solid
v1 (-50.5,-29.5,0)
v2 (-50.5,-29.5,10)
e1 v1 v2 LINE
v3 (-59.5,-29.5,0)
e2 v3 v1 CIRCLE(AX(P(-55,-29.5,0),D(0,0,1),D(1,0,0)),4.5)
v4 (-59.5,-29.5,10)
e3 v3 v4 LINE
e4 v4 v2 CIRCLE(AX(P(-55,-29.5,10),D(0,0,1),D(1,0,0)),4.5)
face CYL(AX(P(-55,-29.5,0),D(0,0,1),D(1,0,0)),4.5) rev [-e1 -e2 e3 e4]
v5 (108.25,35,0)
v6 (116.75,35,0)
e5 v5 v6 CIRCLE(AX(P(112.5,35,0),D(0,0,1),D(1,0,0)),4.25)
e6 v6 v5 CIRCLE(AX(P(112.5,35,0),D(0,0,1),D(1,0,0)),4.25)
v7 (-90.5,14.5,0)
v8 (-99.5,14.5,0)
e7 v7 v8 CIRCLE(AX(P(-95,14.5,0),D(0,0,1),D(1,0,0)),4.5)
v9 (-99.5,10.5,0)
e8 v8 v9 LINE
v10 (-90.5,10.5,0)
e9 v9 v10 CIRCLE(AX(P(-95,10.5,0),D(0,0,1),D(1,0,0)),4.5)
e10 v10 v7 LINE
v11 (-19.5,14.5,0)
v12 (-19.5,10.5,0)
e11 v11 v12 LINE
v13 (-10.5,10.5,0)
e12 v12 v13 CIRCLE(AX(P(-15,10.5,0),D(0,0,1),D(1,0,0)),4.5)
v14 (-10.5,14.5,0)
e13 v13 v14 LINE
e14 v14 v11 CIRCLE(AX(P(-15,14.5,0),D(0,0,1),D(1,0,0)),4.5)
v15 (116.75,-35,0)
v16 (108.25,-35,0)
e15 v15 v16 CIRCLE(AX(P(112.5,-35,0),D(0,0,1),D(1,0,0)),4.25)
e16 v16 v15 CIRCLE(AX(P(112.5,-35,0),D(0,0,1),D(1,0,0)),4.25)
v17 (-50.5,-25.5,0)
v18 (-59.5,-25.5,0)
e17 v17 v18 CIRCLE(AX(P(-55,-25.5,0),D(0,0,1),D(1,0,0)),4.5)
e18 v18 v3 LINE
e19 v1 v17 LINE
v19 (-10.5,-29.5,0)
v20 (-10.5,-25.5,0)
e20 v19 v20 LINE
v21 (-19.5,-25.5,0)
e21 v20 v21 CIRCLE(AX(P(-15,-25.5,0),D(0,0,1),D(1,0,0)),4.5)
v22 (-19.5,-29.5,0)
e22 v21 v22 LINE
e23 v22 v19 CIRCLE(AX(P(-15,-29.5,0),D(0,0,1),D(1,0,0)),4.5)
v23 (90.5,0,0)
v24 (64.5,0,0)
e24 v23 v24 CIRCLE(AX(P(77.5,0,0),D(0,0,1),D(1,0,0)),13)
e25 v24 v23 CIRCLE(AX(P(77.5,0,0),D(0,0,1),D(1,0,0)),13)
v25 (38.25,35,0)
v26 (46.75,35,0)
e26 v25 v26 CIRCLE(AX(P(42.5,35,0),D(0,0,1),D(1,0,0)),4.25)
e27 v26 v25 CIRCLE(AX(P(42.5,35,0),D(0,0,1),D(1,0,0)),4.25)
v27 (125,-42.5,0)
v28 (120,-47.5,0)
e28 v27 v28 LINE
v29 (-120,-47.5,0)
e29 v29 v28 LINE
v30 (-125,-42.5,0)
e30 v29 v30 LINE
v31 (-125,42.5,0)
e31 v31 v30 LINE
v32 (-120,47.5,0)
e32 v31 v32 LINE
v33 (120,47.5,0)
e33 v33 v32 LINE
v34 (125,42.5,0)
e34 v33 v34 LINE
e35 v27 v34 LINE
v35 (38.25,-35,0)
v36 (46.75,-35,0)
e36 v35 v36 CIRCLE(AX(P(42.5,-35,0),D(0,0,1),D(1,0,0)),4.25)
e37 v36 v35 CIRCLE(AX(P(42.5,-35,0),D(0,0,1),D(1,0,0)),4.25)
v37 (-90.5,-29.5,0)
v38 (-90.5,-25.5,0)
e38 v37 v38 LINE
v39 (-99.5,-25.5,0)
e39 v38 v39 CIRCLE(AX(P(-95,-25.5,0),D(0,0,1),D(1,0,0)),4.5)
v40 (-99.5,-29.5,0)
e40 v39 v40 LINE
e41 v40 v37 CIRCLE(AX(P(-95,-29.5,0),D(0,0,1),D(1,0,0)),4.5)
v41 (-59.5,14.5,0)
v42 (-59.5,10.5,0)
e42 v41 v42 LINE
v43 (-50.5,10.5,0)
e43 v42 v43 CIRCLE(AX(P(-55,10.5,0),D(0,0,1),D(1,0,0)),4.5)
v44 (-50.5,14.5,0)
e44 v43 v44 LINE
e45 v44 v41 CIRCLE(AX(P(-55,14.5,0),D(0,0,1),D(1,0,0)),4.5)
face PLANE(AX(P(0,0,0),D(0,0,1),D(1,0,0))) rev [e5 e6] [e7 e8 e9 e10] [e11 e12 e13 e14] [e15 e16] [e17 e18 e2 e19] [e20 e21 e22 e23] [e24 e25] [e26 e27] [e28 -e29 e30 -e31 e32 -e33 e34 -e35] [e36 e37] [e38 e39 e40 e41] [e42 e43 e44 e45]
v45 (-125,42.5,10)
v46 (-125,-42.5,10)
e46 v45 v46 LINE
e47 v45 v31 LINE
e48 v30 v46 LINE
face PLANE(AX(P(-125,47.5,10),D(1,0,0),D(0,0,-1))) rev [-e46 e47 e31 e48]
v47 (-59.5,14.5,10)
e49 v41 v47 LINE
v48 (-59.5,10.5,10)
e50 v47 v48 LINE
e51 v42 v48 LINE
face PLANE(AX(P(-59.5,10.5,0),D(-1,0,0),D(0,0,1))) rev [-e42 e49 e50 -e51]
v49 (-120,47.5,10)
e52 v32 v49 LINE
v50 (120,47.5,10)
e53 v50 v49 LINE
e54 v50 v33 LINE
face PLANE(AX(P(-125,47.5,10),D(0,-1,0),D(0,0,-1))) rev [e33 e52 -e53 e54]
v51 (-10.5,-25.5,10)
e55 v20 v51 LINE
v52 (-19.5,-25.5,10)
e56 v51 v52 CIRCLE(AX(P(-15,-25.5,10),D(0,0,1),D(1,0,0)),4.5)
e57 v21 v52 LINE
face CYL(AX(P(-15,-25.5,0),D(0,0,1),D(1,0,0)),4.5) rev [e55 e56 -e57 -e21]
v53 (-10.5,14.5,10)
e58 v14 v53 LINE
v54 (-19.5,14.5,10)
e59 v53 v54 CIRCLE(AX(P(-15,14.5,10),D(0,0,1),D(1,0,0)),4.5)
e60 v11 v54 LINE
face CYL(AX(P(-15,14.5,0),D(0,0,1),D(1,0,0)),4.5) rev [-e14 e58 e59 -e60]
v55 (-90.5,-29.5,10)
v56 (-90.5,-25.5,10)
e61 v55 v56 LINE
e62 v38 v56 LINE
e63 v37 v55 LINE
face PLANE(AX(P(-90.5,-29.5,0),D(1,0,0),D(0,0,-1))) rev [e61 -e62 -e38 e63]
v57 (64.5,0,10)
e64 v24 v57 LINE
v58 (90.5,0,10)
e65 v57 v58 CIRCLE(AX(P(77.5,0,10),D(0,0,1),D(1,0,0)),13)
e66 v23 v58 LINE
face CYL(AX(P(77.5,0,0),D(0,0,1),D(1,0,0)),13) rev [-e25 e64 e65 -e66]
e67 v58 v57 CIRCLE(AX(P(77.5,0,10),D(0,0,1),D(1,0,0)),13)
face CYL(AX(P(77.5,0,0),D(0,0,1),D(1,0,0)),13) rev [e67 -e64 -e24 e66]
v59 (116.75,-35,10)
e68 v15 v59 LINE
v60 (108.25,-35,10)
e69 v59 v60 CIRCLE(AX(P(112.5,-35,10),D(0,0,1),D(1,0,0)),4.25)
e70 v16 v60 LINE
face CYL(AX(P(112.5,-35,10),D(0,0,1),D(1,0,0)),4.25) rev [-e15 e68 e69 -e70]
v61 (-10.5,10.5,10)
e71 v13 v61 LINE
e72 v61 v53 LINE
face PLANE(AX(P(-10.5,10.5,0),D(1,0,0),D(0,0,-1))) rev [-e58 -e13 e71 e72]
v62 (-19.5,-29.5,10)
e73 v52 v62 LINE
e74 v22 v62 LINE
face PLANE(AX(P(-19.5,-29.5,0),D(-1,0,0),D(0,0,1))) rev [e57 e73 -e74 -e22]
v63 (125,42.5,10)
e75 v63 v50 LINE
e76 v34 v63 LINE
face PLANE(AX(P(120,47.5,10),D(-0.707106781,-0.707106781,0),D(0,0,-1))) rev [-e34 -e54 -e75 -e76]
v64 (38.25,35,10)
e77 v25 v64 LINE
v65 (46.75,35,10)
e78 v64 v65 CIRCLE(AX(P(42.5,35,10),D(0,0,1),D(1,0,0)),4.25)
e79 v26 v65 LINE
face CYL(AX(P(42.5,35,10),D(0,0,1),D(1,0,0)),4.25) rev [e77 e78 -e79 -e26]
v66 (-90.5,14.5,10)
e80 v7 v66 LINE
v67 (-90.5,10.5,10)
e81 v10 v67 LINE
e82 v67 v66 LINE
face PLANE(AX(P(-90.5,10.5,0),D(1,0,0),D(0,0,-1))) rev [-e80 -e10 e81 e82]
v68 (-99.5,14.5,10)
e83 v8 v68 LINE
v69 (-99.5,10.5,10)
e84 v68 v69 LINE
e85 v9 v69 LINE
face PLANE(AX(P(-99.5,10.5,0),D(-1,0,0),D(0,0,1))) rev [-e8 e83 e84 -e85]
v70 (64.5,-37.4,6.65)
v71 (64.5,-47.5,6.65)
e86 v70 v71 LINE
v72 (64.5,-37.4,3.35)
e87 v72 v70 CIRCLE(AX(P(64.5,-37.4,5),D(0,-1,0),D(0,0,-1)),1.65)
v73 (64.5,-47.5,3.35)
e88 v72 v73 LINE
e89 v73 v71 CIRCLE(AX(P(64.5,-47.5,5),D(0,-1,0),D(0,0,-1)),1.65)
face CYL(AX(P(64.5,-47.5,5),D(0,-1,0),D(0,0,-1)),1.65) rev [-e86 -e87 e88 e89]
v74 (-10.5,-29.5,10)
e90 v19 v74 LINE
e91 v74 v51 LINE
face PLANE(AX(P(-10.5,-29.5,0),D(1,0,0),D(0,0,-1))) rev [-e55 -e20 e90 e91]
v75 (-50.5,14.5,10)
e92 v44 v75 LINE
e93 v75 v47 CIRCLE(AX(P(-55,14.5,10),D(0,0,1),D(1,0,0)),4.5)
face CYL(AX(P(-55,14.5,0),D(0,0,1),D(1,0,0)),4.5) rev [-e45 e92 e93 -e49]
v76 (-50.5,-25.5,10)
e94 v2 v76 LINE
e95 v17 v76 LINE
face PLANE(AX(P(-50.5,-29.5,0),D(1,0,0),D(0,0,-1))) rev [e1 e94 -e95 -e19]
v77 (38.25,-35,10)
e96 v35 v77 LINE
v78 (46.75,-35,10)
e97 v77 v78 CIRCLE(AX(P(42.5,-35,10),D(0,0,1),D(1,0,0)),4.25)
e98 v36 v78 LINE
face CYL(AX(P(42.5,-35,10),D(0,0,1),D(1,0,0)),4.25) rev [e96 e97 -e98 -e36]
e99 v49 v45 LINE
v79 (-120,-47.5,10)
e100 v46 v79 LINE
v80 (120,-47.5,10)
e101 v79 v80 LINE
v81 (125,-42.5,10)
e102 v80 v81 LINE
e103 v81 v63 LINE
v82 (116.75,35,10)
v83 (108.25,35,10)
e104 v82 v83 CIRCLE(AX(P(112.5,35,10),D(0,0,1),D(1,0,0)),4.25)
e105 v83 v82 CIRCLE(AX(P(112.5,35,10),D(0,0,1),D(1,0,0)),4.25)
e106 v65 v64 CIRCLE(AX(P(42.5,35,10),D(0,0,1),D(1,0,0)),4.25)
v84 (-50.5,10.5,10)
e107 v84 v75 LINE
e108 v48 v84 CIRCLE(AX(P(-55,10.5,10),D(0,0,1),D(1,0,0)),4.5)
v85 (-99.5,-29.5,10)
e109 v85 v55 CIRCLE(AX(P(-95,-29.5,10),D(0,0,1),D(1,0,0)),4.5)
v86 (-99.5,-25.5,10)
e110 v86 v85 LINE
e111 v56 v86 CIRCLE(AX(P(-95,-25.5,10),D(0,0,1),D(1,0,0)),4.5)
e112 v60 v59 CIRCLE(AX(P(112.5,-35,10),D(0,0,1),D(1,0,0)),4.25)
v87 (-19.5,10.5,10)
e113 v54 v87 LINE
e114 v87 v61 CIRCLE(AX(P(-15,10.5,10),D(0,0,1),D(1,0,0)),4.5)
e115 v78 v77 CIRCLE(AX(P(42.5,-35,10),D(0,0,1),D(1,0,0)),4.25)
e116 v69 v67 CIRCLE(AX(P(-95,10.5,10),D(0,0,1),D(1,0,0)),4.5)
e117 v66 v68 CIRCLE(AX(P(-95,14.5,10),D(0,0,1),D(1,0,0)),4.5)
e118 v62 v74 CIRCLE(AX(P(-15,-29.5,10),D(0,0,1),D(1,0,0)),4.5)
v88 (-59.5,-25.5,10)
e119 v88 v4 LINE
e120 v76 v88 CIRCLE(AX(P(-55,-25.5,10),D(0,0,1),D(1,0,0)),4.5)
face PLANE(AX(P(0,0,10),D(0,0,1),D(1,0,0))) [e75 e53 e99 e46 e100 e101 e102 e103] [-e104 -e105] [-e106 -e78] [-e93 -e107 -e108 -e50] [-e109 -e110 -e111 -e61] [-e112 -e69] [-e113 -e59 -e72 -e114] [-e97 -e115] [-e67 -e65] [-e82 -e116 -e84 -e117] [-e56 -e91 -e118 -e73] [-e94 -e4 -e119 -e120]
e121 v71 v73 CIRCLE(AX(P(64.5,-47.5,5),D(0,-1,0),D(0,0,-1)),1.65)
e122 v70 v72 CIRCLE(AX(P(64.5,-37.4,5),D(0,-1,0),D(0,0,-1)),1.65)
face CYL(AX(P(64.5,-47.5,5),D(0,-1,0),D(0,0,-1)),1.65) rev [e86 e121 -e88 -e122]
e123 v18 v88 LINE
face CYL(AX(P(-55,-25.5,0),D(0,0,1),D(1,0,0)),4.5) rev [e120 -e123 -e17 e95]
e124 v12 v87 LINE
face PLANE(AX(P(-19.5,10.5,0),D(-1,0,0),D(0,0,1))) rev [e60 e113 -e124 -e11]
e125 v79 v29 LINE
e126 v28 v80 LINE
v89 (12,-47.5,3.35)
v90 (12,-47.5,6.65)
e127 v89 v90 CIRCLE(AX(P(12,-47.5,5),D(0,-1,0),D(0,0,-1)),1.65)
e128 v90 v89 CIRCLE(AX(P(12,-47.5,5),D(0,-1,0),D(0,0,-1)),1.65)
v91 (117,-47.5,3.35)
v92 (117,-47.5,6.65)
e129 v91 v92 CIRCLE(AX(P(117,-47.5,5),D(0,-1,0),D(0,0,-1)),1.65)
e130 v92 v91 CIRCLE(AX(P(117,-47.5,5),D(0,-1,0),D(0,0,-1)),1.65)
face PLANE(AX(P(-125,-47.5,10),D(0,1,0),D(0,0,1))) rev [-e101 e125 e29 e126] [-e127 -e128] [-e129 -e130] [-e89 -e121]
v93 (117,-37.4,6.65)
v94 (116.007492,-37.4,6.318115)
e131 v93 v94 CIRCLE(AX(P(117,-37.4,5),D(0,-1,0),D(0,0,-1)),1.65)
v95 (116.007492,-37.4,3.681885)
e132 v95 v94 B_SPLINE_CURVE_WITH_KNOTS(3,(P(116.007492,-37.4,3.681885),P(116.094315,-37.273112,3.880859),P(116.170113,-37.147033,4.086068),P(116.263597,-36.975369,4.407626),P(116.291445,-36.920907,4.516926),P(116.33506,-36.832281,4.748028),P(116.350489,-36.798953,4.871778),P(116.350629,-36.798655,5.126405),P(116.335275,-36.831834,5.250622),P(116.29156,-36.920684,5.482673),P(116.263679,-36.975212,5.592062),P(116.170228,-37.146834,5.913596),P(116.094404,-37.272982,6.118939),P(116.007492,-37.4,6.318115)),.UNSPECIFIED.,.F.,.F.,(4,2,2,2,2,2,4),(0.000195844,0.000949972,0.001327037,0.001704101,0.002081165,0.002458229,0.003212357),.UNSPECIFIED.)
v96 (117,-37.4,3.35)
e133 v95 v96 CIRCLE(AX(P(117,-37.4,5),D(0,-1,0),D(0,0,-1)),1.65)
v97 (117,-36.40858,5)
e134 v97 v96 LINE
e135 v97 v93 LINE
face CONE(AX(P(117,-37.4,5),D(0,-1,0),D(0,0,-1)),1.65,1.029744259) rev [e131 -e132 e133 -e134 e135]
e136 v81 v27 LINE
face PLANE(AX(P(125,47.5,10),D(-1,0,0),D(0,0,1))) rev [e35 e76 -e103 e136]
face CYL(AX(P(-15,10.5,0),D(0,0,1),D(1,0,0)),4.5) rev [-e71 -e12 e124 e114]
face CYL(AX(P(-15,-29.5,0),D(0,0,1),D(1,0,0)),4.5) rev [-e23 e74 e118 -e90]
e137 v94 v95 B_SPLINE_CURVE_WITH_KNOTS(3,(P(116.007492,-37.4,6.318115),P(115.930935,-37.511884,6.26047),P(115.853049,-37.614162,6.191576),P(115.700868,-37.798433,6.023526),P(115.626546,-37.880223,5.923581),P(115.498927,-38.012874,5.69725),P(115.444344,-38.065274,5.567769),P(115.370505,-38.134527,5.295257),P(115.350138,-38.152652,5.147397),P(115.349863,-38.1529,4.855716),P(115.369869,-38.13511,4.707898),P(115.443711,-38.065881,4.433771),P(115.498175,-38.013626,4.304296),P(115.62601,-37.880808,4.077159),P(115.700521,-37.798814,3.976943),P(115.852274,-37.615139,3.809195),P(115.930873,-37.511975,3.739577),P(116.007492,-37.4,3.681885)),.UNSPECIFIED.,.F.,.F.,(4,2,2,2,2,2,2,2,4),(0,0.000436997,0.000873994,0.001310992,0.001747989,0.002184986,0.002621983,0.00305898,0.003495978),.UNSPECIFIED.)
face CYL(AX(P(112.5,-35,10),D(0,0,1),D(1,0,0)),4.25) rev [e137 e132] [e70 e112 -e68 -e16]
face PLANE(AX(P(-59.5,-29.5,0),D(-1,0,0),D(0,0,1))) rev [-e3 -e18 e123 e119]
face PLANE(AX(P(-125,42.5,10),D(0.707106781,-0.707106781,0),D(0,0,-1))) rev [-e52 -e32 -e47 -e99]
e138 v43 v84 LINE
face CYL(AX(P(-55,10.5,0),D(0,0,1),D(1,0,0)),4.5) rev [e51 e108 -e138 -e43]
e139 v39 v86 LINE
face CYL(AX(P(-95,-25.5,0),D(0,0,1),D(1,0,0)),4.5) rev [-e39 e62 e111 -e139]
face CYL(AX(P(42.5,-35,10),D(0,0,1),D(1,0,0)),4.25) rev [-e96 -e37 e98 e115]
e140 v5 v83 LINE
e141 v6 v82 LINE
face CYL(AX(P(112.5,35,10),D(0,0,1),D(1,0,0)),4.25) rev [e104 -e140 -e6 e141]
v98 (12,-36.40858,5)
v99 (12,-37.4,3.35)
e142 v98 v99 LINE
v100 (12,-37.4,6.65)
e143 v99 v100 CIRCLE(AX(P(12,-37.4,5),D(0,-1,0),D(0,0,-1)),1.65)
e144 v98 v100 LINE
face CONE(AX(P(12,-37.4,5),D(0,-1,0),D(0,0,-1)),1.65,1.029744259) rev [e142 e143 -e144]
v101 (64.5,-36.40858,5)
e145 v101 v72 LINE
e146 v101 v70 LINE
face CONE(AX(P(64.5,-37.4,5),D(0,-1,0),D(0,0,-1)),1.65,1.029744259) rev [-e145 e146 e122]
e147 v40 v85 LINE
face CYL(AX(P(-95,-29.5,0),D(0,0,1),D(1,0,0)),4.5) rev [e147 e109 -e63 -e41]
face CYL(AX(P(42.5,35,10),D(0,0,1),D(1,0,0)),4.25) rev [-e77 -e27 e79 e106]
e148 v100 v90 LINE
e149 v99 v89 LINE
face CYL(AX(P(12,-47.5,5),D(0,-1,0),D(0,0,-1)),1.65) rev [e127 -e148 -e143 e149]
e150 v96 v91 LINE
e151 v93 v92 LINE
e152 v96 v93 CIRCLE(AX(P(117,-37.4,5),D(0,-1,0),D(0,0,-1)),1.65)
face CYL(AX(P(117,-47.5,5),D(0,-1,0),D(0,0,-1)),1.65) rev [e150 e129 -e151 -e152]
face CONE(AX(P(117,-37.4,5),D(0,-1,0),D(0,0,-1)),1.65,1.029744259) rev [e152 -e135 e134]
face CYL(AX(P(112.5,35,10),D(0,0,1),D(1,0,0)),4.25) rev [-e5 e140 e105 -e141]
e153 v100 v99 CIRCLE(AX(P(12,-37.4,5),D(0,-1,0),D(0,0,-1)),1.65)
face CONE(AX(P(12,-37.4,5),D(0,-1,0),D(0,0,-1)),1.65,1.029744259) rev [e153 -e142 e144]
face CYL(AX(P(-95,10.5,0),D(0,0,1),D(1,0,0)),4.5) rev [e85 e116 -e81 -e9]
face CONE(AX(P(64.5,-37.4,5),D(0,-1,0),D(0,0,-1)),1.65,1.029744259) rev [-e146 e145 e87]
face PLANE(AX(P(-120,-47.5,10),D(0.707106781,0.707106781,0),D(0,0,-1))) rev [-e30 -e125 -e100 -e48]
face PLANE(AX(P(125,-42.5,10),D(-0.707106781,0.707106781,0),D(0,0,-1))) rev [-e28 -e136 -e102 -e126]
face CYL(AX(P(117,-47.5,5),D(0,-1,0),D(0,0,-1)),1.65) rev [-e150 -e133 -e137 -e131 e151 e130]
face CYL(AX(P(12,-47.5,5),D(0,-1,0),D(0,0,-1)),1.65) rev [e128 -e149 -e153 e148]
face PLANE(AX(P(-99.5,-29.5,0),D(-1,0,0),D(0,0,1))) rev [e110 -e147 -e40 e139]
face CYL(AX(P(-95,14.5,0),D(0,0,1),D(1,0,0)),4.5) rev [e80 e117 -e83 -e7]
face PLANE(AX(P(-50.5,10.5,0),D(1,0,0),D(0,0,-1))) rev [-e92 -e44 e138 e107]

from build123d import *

# Parameters (mm, degrees)
SKETCH_1_W                  = 250
SKETCH_1_H                  = 95
EXTRUDE_1_DEPTH             = 10
CUT_EXTRUDE_2_DEPTH         = 135.094183319
PATTERN_LINEAR_1_COUNT      = 2
PATTERN_LINEAR_1_PITCH      = 40
PATTERN_LINEAR_1_COUNT_DIR2 = 2
PATTERN_LINEAR_1_PITCH_DIR2 = 40
PATTERN_LINEAR_2_COUNT      = 2
PATTERN_LINEAR_2_PITCH      = 40
PATTERN_LINEAR_2_COUNT_DIR2 = 2
PATTERN_LINEAR_2_PITCH_DIR2 = 40
CHAMFER_1_SIZE              = 5
HOLE_WIZARD_M10_3_D         = 8.5
HOLE_WIZARD_M10_3_DEPTH     = 24.5
HOLE_WIZARD_M10_3_TIP       = 2.553657631
SKETCH_12_R                 = 13
CUT_EXTRUDE_5_DEPTH         = 135.094183319
HOLE_WIZARD_M4_1_D          = 3.3
HOLE_WIZARD_M4_1_DEPTH      = 10.1
HOLE_WIZARD_M4_1_TIP        = 0.991420021


with BuildPart() as part:
    # 草图1 → 凸台-拉伸1 (new body)
    with BuildSketch(Plane.XY):
        Rectangle(SKETCH_1_W, SKETCH_1_H)
    extrude(amount=EXTRUDE_1_DEPTH)

    # 草图3 → 切除-拉伸2 (cut, through all)
    with BuildSketch(Plane.XY.offset(10)):
        with BuildLine():
            Line((-59.5, -29.5), (-59.5, -25.5))
            ThreePointArc((-59.5, -25.5), (-55, -21), (-50.5, -25.5))
            Line((-50.5, -25.5), (-50.5, -29.5))
            ThreePointArc((-50.5, -29.5), (-55, -34), (-59.5, -29.5))
        make_face()
    cut_extrude_2 = extrude(amount=-CUT_EXTRUDE_2_DEPTH, mode=Mode.SUBTRACT)

    # 阵列(线性)1: Cut-Extrude 2 2 × 2
    with Locations(*[(i * PATTERN_LINEAR_1_PITCH, j * PATTERN_LINEAR_1_PITCH_DIR2, 0) for i in range(PATTERN_LINEAR_1_COUNT) for j in range(PATTERN_LINEAR_1_COUNT_DIR2) if (i, j) != (0, 0)]):
        add(cut_extrude_2, mode=Mode.SUBTRACT)

    # 阵列(线性)2: Cut-Extrude 2 2 × 2
    with Locations(*[(-i * PATTERN_LINEAR_2_PITCH, j * PATTERN_LINEAR_2_PITCH_DIR2, 0) for i in range(PATTERN_LINEAR_2_COUNT) for j in range(PATTERN_LINEAR_2_COUNT_DIR2) if (i, j) != (0, 0)]):
        add(cut_extrude_2, mode=Mode.SUBTRACT)

    # 倒角1
    chamfer_1_edges = [part.edges().sort_by_distance(p)[0] for p in [
        (125, -47.5, 5),
        (-125, -47.5, 5),
        (-125, 47.5, 5),
        (125, 47.5, 5),
    ]]
    chamfer(chamfer_1_edges, length=CHAMFER_1_SIZE)

    # M10 螺纹孔3
    with Locations(Plane(origin=(42.5, 35, 10), x_dir=(1, 0, 0), z_dir=(0, 0, 1))):
        with Locations((0, 0), (70, 0), (70, -70), (0, -70)):
            Hole(HOLE_WIZARD_M10_3_D / 2, depth=HOLE_WIZARD_M10_3_DEPTH)
            with Locations((0, 0, -(HOLE_WIZARD_M10_3_DEPTH + HOLE_WIZARD_M10_3_TIP / 2))):  # 118° drill point
                Cone(0, HOLE_WIZARD_M10_3_D / 2, HOLE_WIZARD_M10_3_TIP, mode=Mode.SUBTRACT)

    # 草图12 → 切除-拉伸5 (cut, through all)
    with BuildSketch(Plane.XY.offset(10)):
        with Locations((77.5, 0)):
            Circle(SKETCH_12_R)
    extrude(amount=-CUT_EXTRUDE_5_DEPTH, mode=Mode.SUBTRACT)

    # M4 螺纹孔1
    with Locations(Plane(origin=(117, -47.5, 5), x_dir=(0, 0, -1), z_dir=(0, -1, 0))):
        with Locations((0, 0), (0, -105), (0, -52.5)):
            Hole(HOLE_WIZARD_M4_1_D / 2, depth=HOLE_WIZARD_M4_1_DEPTH)
            with Locations((0, 0, -(HOLE_WIZARD_M4_1_DEPTH + HOLE_WIZARD_M4_1_TIP / 2))):  # 118° drill point
                Cone(0, HOLE_WIZARD_M4_1_D / 2, HOLE_WIZARD_M4_1_TIP, mode=Mode.SUBTRACT)


solid = part.part
